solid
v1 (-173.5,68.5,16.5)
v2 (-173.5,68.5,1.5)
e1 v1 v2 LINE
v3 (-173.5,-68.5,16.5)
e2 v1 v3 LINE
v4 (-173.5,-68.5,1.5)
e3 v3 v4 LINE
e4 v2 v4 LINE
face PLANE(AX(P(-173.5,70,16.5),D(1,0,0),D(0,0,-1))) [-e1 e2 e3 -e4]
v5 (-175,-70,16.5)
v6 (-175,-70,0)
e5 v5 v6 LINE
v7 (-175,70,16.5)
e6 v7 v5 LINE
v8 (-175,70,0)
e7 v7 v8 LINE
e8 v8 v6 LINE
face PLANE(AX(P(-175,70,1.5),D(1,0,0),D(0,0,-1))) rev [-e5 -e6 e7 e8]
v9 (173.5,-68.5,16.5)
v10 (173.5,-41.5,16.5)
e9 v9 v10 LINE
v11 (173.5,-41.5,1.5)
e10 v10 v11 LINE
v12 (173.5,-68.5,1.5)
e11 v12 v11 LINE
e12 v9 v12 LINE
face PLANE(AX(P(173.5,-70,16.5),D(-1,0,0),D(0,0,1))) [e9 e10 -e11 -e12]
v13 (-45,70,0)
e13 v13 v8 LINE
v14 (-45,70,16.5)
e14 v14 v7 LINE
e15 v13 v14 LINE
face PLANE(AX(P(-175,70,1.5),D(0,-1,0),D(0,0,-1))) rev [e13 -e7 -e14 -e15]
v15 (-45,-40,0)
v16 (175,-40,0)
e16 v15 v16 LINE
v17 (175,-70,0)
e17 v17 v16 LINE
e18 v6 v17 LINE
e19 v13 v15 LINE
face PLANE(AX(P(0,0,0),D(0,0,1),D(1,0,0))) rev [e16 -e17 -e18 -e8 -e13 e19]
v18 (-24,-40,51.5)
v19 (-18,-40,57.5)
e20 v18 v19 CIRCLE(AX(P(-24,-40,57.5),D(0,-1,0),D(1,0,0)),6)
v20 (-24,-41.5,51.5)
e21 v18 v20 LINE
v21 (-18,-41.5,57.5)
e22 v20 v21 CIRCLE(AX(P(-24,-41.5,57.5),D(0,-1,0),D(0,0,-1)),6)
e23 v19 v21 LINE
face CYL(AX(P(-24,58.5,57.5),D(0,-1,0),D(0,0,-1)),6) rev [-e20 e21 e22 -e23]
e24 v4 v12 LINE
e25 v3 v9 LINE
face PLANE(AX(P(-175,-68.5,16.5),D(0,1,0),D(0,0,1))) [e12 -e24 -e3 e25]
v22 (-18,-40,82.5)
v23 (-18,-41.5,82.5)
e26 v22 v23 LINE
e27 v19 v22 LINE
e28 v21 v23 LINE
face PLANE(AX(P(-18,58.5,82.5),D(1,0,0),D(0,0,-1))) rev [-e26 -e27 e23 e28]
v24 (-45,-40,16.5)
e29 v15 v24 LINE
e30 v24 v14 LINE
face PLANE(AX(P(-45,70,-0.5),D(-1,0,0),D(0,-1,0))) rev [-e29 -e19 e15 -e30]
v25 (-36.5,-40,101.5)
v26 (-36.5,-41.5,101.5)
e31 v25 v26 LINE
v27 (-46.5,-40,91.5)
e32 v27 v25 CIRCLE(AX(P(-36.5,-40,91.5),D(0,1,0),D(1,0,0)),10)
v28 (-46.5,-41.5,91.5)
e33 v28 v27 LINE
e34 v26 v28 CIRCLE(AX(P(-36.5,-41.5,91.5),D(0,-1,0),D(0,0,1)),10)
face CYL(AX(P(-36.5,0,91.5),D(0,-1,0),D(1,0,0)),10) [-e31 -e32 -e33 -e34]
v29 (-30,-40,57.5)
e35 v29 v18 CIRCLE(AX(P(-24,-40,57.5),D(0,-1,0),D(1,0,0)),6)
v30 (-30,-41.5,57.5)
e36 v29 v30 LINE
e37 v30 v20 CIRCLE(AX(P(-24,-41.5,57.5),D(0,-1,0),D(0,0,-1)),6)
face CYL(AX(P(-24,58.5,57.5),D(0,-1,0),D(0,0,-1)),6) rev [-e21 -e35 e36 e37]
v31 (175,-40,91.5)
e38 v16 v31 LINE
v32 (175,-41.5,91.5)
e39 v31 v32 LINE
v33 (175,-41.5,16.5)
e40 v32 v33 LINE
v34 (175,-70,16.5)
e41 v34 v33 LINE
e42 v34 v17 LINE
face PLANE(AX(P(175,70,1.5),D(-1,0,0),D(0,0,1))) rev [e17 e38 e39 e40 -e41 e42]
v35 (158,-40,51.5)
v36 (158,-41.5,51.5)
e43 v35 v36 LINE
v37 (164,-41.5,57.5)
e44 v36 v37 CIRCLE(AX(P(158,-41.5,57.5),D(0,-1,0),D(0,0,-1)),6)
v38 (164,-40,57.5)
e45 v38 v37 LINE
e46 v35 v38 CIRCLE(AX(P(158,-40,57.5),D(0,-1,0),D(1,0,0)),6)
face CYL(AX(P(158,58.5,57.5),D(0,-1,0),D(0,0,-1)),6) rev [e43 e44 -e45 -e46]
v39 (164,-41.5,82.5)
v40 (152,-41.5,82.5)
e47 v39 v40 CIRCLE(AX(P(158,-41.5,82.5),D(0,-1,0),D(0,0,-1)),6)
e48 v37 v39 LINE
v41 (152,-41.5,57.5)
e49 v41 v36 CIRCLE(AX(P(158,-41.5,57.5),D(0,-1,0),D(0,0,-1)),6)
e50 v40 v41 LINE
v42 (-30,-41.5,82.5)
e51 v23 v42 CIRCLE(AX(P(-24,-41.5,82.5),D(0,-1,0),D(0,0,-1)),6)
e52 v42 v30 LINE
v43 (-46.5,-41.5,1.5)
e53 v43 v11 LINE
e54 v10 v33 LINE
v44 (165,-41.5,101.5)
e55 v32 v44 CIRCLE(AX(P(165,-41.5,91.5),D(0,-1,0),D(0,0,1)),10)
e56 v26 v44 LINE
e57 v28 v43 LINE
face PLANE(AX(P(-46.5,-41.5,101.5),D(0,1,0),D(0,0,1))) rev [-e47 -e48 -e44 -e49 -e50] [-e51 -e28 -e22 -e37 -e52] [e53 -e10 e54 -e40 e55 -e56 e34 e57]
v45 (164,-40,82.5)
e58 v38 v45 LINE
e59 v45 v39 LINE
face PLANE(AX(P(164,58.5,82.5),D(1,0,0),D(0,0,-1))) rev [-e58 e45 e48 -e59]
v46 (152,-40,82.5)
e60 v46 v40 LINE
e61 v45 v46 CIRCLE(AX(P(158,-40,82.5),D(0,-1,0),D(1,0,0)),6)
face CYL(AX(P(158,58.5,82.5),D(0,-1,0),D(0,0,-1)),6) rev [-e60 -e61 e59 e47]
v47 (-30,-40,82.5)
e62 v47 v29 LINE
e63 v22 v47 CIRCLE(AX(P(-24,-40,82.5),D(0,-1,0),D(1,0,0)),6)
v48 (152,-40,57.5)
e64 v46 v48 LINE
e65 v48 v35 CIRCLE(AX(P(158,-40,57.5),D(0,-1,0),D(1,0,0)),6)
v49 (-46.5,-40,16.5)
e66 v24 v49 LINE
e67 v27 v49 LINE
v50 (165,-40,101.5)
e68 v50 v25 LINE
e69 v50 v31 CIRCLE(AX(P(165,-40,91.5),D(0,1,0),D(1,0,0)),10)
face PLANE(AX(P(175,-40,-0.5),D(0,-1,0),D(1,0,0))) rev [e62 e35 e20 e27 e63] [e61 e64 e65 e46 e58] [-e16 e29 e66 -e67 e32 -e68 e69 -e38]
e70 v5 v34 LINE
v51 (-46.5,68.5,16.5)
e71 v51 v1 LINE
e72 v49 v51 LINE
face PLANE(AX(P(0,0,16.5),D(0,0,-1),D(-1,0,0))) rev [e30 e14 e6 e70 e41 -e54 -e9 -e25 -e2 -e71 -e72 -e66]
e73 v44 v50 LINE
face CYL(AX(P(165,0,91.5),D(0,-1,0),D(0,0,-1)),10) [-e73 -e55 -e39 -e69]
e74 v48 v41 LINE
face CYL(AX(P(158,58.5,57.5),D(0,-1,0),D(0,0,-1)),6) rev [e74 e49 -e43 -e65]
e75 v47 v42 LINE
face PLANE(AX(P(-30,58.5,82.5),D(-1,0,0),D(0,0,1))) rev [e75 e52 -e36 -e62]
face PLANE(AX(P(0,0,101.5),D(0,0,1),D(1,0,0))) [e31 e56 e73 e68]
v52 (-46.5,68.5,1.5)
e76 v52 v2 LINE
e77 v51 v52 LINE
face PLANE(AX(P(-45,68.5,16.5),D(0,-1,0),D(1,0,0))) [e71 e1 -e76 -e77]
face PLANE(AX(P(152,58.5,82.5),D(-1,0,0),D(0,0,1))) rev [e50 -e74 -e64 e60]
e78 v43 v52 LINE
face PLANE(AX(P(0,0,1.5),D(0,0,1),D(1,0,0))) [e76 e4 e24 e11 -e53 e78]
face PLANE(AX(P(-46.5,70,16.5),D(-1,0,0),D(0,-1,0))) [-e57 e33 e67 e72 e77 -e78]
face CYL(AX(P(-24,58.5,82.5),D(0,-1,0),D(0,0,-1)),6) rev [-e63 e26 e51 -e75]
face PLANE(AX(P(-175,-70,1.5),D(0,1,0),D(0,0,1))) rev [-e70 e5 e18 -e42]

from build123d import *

# Parameters (mm, degrees)
SKETCH_1_W          = 350
SKETCH_1_H          = 140
EXTRUDE_1_DEPTH     = 1.5
SKETCH_2_W          = 220
SKETCH_2_H          = 110
CUT_EXTRUDE_1_DEPTH = 2
EXTRUDE_1_2_DEPTH   = 15
SKETCH_4_W          = 221.5
SKETCH_4_H          = 1.5
EXTRUDE_3_DEPTH     = 100
FILLET_1_R          = 10
CUT_EXTRUDE_2_DEPTH = 100


with BuildPart() as part:
    # 草图1 → Extrude 1 (new body)
    with BuildSketch(Plane.XY):
        Rectangle(SKETCH_1_W, SKETCH_1_H)
    extrude(amount=EXTRUDE_1_DEPTH)

    # 草图2 → 切除-拉伸1 (cut)
    with BuildSketch(Plane.XY.offset(1.5)):
        with Locations((65, 15)):
            Rectangle(SKETCH_2_W, SKETCH_2_H)
    extrude(amount=-CUT_EXTRUDE_1_DEPTH, mode=Mode.SUBTRACT)

    # 草图3 → Extrude 1 2 (add)
    with BuildSketch(Plane.XY.offset(1.5)):
        Polygon((175, -40), (175, -70), (-175, -70), (-175, 70), (-45, 70), (-45, -40), (-46.5, -40), (-46.5, 68.5), (-173.5, 68.5), (-173.5, -68.5), (173.5, -68.5), (173.5, -40), align=None)
    extrude(amount=EXTRUDE_1_2_DEPTH)

    # 草图4 → 凸台-拉伸3 (add)
    with BuildSketch(Plane.XY.offset(1.5)):
        with Locations((64.25, -40.75)):
            Rectangle(SKETCH_4_W, SKETCH_4_H)
    extrude(amount=EXTRUDE_3_DEPTH)

    # 圆角1
    fillet_1_edges = [part.edges().sort_by_distance(p)[0] for p in [
        (-46.5, -40.75, 101.5),
        (175, -40.75, 101.5),
    ]]
    fillet(fillet_1_edges, radius=FILLET_1_R)

    # 草图5 → 切除-拉伸2 (cut)
    with BuildSketch(Plane.XZ.offset(41.5)):
        with BuildLine():
            Line((-18, 82.5), (-18, 57.5))
            ThreePointArc((-18, 57.5), (-24, 51.5), (-30, 57.5))
            Line((-30, 57.5), (-30, 82.5))
            ThreePointArc((-30, 82.5), (-24, 88.5), (-18, 82.5))
        make_face()
        with BuildLine():
            Line((164, 82.5), (164, 57.5))
            ThreePointArc((164, 57.5), (158, 51.5), (152, 57.5))
            Line((152, 57.5), (152, 82.5))
            ThreePointArc((152, 82.5), (158, 88.5), (164, 82.5))
        make_face()
    extrude(amount=-CUT_EXTRUDE_2_DEPTH, mode=Mode.SUBTRACT)


solid = part.part
